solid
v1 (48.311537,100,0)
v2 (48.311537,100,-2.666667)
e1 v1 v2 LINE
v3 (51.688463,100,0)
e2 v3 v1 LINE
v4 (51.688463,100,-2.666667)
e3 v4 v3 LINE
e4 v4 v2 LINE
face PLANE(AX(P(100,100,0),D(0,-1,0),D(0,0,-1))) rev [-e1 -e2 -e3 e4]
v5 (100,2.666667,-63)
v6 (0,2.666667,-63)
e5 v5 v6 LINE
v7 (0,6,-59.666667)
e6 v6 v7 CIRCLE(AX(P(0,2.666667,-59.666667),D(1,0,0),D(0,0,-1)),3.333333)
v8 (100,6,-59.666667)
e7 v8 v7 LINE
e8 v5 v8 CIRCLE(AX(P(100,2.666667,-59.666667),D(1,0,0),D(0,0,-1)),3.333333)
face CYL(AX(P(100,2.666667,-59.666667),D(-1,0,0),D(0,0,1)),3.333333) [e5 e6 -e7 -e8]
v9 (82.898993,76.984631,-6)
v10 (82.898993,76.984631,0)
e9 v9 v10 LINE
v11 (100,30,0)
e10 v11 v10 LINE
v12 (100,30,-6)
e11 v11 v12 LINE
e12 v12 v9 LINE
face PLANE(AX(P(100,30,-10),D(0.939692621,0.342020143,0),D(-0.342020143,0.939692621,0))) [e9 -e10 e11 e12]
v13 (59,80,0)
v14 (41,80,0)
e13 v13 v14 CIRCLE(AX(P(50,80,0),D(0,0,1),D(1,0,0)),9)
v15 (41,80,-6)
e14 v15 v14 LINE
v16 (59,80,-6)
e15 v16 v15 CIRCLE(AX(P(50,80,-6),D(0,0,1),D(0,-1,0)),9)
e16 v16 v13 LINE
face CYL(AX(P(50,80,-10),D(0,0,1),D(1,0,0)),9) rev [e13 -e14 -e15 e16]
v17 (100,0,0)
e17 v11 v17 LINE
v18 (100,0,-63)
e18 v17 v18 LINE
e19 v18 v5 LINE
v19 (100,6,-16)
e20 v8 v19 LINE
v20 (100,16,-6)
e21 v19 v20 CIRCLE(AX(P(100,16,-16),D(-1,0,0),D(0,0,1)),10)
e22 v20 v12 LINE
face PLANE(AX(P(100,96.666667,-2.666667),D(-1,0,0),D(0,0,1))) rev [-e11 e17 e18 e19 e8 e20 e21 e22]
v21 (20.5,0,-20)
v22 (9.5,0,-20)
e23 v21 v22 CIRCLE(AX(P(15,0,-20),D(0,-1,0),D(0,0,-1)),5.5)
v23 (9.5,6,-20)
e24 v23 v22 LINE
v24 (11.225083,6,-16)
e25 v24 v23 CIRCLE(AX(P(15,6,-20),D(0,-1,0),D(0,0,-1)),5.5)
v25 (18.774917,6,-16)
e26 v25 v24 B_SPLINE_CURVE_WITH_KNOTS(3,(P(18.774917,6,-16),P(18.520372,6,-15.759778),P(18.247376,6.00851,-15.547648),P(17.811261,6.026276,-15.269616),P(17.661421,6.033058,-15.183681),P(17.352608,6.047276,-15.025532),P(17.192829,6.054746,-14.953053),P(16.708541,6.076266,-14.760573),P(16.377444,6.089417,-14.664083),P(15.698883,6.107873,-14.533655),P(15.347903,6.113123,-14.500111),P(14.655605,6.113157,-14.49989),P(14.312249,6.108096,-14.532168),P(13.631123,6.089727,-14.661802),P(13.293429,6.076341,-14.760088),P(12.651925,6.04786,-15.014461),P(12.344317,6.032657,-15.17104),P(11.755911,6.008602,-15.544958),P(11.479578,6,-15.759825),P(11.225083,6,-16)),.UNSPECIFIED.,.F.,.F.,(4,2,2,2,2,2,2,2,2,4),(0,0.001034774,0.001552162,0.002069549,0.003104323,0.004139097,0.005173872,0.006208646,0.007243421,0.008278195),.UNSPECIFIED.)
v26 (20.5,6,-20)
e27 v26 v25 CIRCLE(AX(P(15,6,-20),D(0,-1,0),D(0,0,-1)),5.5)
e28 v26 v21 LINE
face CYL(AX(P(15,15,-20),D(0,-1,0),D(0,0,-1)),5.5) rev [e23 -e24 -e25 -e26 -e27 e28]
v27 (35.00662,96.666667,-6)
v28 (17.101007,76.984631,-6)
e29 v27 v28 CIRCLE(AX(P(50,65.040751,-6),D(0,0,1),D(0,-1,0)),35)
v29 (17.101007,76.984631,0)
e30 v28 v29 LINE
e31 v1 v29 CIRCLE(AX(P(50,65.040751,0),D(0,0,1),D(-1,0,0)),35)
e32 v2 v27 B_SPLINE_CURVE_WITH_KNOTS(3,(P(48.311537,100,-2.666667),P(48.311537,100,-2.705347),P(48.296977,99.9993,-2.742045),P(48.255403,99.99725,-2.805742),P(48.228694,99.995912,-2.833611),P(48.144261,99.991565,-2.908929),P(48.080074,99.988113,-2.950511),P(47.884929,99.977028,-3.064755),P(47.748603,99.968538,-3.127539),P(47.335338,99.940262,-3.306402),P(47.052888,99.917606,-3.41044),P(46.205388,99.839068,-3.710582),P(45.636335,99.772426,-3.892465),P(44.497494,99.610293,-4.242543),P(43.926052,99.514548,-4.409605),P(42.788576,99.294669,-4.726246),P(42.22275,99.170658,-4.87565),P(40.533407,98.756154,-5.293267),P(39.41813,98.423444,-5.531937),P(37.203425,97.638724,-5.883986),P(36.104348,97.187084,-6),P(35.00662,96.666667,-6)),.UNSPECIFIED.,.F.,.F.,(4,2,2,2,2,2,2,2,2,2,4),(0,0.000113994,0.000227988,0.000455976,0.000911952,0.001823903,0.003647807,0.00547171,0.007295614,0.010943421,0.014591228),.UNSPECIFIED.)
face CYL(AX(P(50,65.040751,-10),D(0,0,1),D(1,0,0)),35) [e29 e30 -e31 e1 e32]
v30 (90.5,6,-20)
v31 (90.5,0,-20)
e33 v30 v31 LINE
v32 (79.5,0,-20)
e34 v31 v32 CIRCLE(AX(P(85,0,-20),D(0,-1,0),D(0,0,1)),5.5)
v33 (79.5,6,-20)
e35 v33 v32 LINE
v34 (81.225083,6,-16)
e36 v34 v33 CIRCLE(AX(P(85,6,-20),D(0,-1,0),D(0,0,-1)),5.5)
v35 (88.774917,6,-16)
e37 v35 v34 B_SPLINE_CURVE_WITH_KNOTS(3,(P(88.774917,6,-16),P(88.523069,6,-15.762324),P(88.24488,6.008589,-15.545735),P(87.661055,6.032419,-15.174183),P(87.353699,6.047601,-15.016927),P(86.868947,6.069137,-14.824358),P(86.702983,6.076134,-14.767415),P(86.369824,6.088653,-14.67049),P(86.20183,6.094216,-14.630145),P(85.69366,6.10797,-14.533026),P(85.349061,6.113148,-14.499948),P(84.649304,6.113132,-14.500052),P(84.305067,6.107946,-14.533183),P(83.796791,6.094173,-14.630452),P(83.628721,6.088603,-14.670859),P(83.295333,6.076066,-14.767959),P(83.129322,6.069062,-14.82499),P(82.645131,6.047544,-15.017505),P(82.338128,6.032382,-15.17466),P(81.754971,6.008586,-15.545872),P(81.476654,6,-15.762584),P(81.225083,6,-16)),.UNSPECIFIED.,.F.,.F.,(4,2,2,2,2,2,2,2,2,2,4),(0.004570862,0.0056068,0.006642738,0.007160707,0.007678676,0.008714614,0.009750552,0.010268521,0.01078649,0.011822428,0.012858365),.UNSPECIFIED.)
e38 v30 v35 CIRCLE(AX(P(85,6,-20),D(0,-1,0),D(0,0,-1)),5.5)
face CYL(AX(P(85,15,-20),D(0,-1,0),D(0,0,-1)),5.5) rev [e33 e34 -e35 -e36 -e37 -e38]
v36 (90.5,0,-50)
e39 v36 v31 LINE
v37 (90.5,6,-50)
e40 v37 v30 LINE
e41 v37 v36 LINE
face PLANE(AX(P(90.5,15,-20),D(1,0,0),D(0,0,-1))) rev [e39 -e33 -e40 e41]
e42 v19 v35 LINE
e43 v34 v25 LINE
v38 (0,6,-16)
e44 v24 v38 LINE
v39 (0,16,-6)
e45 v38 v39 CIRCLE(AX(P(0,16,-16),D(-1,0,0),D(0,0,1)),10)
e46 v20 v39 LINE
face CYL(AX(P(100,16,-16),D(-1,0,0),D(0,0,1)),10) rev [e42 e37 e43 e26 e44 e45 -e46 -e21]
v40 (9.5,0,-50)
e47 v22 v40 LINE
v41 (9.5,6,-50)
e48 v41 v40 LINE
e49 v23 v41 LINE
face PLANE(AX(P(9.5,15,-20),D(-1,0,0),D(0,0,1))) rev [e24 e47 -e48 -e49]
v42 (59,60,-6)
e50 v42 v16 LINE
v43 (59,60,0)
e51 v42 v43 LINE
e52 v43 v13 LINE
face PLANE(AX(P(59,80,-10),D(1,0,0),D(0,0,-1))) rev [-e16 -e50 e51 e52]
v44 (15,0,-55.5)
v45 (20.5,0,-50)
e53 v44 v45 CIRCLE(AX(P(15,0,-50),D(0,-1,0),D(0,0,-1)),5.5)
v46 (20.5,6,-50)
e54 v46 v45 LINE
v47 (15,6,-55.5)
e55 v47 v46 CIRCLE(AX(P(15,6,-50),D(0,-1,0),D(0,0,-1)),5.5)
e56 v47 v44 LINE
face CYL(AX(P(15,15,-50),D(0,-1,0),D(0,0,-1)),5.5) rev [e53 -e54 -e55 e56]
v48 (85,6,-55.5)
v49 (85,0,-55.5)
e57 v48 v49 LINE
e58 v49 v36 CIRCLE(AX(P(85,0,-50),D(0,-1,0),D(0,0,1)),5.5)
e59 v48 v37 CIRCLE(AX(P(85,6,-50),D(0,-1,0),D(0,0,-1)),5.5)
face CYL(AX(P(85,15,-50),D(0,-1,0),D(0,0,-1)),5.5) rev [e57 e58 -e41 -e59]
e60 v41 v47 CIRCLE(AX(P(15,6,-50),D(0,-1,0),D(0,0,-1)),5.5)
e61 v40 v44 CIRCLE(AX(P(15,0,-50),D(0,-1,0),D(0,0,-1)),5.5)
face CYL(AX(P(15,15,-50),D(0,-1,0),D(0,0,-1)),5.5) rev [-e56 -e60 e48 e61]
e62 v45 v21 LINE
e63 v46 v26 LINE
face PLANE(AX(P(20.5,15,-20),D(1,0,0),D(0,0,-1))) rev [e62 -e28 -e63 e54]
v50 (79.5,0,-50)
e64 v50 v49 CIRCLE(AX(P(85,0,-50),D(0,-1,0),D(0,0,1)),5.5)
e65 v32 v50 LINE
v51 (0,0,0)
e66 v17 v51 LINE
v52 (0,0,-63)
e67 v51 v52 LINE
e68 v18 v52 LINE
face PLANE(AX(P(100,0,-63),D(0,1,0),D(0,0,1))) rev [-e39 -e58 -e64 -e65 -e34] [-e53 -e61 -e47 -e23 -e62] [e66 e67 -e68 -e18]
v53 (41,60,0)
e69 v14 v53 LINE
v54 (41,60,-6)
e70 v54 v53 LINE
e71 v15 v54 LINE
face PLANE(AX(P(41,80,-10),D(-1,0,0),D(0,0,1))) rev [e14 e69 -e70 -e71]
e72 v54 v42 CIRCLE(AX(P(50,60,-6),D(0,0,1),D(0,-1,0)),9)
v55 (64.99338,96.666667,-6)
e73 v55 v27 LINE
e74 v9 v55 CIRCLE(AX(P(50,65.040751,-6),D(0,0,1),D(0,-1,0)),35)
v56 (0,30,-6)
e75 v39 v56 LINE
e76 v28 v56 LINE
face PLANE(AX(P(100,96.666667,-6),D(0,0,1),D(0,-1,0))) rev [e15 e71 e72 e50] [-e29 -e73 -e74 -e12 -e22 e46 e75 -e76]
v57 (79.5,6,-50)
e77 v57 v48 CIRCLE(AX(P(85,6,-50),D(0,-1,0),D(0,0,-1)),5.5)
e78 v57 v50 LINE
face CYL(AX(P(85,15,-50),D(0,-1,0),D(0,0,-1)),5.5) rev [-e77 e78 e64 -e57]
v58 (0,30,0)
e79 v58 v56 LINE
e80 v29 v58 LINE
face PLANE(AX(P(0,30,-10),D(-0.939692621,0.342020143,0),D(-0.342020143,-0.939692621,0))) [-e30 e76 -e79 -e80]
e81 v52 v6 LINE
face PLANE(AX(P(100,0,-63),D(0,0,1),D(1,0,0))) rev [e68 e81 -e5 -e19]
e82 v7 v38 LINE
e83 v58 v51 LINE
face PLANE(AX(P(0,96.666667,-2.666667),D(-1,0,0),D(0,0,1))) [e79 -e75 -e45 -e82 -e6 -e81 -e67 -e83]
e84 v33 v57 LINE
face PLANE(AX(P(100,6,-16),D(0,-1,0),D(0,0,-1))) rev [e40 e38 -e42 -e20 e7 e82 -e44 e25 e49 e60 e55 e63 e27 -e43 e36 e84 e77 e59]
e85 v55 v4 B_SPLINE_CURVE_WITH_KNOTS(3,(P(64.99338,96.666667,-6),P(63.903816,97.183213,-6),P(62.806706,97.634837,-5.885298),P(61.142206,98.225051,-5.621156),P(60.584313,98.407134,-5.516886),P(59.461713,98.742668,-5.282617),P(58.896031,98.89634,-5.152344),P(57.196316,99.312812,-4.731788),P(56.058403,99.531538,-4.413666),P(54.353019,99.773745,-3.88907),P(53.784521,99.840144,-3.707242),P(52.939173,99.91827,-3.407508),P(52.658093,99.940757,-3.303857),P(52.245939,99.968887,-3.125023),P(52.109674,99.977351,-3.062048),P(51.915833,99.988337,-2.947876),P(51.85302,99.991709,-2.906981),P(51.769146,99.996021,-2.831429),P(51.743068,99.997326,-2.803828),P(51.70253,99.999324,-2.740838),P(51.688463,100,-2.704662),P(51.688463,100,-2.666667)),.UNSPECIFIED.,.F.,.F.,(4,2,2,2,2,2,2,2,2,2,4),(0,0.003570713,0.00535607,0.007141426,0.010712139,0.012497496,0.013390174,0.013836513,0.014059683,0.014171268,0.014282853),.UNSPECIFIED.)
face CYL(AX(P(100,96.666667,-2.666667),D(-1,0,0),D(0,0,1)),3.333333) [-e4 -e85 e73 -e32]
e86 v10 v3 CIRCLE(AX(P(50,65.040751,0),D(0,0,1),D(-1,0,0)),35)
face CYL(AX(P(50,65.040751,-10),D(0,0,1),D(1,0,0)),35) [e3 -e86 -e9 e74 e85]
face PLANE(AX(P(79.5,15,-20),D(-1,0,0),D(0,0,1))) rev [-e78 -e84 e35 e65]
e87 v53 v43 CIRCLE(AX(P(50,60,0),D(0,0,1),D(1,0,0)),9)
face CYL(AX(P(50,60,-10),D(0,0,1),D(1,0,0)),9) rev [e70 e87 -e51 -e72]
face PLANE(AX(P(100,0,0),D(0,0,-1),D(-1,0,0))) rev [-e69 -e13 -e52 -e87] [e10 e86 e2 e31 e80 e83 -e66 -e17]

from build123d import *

# Parameters (mm, degrees)
HOT_ROLLED_UNEQUAL_ANGLE_GB_T706_2008_10_DEPTH = 100
SKETCH3_OUTSIDE_W                              = 132.964
SKETCH3_OUTSIDE_H                              = 132.964
CUT_EXTRUDE1_DEPTH                             = 10
CUT_EXTRUDE2_DEPTH                             = 15


with BuildPart() as part:
    # Sketch1 → Hot-rolled unequal angle gb∕t706-2008 100 X 63 X 6(1) (new body)
    with BuildSketch(Plane(origin=(0, 0, 0), x_dir=(0, 0, -1), z_dir=(1, 0, 0))):
        with BuildLine():
            Line((0, 0), (0, 100))
            Line((0, 100), (2.666666667, 100))
            ThreePointArc((2.666666667, 100), (5.023689271, 99.023689271), (6, 96.666666667))
            Line((6, 96.666666667), (6, 16))
            ThreePointArc((6, 16), (8.928932188, 8.928932188), (16, 6))
            Line((16, 6), (59.666666667, 6))
            ThreePointArc((59.666666667, 6), (62.023689271, 5.023689271), (63, 2.666666667))
            Line((63, 2.666666667), (63, 0))
            Line((63, 0), (0, 0))
        make_face()
    extrude(amount=HOT_ROLLED_UNEQUAL_ANGLE_GB_T706_2008_10_DEPTH)

    # Sketch3 outside → Cut-Extrude1 (cut)
    # profile 1 of 2: a face of its own
    with BuildSketch(Plane.XY):
        with Locations((50, 50)):
            Rectangle(SKETCH3_OUTSIDE_W, SKETCH3_OUTSIDE_H)
        with BuildLine():
            Line((0, 30), (17.101007166, 76.984631039))
            ThreePointArc((17.101007166, 76.984631039), (50, 100.040750994), (82.898992834, 76.984631039))
            Line((82.898992834, 76.984631039), (100, 30))
            Line((100, 30), (100, 0))
            Line((100, 0), (0, 0))
            Line((0, 0), (0, 30))
        make_face(mode=Mode.SUBTRACT)
    # profile 2 of 2: a face of its own
    with BuildSketch(Plane.XY):
        with BuildLine():
            Line((59, 80), (59, 60))
            ThreePointArc((59, 60), (50, 51), (41, 60))
            Line((41, 60), (41, 80))
            ThreePointArc((41, 80), (50, 89), (59, 80))
        make_face()
    extrude(amount=-CUT_EXTRUDE1_DEPTH, mode=Mode.SUBTRACT)

    # Sketch4 → Cut-Extrude2 (cut)
    with BuildSketch(Plane.XZ):
        with BuildLine():
            Line((20.5, -20), (20.5, -50))
            ThreePointArc((20.5, -50), (15, -55.5), (9.5, -50))
            Line((9.5, -50), (9.5, -20))
            ThreePointArc((9.5, -20), (15, -14.5), (20.5, -20))
        make_face()
        with BuildLine():
            Line((79.5, -20), (79.5, -50))
            ThreePointArc((79.5, -50), (85, -55.5), (90.5, -50))
            Line((90.5, -50), (90.5, -20))
            ThreePointArc((90.5, -20), (85, -14.5), (79.5, -20))
        make_face()
    extrude(amount=-CUT_EXTRUDE2_DEPTH, mode=Mode.SUBTRACT)


solid = part.part
